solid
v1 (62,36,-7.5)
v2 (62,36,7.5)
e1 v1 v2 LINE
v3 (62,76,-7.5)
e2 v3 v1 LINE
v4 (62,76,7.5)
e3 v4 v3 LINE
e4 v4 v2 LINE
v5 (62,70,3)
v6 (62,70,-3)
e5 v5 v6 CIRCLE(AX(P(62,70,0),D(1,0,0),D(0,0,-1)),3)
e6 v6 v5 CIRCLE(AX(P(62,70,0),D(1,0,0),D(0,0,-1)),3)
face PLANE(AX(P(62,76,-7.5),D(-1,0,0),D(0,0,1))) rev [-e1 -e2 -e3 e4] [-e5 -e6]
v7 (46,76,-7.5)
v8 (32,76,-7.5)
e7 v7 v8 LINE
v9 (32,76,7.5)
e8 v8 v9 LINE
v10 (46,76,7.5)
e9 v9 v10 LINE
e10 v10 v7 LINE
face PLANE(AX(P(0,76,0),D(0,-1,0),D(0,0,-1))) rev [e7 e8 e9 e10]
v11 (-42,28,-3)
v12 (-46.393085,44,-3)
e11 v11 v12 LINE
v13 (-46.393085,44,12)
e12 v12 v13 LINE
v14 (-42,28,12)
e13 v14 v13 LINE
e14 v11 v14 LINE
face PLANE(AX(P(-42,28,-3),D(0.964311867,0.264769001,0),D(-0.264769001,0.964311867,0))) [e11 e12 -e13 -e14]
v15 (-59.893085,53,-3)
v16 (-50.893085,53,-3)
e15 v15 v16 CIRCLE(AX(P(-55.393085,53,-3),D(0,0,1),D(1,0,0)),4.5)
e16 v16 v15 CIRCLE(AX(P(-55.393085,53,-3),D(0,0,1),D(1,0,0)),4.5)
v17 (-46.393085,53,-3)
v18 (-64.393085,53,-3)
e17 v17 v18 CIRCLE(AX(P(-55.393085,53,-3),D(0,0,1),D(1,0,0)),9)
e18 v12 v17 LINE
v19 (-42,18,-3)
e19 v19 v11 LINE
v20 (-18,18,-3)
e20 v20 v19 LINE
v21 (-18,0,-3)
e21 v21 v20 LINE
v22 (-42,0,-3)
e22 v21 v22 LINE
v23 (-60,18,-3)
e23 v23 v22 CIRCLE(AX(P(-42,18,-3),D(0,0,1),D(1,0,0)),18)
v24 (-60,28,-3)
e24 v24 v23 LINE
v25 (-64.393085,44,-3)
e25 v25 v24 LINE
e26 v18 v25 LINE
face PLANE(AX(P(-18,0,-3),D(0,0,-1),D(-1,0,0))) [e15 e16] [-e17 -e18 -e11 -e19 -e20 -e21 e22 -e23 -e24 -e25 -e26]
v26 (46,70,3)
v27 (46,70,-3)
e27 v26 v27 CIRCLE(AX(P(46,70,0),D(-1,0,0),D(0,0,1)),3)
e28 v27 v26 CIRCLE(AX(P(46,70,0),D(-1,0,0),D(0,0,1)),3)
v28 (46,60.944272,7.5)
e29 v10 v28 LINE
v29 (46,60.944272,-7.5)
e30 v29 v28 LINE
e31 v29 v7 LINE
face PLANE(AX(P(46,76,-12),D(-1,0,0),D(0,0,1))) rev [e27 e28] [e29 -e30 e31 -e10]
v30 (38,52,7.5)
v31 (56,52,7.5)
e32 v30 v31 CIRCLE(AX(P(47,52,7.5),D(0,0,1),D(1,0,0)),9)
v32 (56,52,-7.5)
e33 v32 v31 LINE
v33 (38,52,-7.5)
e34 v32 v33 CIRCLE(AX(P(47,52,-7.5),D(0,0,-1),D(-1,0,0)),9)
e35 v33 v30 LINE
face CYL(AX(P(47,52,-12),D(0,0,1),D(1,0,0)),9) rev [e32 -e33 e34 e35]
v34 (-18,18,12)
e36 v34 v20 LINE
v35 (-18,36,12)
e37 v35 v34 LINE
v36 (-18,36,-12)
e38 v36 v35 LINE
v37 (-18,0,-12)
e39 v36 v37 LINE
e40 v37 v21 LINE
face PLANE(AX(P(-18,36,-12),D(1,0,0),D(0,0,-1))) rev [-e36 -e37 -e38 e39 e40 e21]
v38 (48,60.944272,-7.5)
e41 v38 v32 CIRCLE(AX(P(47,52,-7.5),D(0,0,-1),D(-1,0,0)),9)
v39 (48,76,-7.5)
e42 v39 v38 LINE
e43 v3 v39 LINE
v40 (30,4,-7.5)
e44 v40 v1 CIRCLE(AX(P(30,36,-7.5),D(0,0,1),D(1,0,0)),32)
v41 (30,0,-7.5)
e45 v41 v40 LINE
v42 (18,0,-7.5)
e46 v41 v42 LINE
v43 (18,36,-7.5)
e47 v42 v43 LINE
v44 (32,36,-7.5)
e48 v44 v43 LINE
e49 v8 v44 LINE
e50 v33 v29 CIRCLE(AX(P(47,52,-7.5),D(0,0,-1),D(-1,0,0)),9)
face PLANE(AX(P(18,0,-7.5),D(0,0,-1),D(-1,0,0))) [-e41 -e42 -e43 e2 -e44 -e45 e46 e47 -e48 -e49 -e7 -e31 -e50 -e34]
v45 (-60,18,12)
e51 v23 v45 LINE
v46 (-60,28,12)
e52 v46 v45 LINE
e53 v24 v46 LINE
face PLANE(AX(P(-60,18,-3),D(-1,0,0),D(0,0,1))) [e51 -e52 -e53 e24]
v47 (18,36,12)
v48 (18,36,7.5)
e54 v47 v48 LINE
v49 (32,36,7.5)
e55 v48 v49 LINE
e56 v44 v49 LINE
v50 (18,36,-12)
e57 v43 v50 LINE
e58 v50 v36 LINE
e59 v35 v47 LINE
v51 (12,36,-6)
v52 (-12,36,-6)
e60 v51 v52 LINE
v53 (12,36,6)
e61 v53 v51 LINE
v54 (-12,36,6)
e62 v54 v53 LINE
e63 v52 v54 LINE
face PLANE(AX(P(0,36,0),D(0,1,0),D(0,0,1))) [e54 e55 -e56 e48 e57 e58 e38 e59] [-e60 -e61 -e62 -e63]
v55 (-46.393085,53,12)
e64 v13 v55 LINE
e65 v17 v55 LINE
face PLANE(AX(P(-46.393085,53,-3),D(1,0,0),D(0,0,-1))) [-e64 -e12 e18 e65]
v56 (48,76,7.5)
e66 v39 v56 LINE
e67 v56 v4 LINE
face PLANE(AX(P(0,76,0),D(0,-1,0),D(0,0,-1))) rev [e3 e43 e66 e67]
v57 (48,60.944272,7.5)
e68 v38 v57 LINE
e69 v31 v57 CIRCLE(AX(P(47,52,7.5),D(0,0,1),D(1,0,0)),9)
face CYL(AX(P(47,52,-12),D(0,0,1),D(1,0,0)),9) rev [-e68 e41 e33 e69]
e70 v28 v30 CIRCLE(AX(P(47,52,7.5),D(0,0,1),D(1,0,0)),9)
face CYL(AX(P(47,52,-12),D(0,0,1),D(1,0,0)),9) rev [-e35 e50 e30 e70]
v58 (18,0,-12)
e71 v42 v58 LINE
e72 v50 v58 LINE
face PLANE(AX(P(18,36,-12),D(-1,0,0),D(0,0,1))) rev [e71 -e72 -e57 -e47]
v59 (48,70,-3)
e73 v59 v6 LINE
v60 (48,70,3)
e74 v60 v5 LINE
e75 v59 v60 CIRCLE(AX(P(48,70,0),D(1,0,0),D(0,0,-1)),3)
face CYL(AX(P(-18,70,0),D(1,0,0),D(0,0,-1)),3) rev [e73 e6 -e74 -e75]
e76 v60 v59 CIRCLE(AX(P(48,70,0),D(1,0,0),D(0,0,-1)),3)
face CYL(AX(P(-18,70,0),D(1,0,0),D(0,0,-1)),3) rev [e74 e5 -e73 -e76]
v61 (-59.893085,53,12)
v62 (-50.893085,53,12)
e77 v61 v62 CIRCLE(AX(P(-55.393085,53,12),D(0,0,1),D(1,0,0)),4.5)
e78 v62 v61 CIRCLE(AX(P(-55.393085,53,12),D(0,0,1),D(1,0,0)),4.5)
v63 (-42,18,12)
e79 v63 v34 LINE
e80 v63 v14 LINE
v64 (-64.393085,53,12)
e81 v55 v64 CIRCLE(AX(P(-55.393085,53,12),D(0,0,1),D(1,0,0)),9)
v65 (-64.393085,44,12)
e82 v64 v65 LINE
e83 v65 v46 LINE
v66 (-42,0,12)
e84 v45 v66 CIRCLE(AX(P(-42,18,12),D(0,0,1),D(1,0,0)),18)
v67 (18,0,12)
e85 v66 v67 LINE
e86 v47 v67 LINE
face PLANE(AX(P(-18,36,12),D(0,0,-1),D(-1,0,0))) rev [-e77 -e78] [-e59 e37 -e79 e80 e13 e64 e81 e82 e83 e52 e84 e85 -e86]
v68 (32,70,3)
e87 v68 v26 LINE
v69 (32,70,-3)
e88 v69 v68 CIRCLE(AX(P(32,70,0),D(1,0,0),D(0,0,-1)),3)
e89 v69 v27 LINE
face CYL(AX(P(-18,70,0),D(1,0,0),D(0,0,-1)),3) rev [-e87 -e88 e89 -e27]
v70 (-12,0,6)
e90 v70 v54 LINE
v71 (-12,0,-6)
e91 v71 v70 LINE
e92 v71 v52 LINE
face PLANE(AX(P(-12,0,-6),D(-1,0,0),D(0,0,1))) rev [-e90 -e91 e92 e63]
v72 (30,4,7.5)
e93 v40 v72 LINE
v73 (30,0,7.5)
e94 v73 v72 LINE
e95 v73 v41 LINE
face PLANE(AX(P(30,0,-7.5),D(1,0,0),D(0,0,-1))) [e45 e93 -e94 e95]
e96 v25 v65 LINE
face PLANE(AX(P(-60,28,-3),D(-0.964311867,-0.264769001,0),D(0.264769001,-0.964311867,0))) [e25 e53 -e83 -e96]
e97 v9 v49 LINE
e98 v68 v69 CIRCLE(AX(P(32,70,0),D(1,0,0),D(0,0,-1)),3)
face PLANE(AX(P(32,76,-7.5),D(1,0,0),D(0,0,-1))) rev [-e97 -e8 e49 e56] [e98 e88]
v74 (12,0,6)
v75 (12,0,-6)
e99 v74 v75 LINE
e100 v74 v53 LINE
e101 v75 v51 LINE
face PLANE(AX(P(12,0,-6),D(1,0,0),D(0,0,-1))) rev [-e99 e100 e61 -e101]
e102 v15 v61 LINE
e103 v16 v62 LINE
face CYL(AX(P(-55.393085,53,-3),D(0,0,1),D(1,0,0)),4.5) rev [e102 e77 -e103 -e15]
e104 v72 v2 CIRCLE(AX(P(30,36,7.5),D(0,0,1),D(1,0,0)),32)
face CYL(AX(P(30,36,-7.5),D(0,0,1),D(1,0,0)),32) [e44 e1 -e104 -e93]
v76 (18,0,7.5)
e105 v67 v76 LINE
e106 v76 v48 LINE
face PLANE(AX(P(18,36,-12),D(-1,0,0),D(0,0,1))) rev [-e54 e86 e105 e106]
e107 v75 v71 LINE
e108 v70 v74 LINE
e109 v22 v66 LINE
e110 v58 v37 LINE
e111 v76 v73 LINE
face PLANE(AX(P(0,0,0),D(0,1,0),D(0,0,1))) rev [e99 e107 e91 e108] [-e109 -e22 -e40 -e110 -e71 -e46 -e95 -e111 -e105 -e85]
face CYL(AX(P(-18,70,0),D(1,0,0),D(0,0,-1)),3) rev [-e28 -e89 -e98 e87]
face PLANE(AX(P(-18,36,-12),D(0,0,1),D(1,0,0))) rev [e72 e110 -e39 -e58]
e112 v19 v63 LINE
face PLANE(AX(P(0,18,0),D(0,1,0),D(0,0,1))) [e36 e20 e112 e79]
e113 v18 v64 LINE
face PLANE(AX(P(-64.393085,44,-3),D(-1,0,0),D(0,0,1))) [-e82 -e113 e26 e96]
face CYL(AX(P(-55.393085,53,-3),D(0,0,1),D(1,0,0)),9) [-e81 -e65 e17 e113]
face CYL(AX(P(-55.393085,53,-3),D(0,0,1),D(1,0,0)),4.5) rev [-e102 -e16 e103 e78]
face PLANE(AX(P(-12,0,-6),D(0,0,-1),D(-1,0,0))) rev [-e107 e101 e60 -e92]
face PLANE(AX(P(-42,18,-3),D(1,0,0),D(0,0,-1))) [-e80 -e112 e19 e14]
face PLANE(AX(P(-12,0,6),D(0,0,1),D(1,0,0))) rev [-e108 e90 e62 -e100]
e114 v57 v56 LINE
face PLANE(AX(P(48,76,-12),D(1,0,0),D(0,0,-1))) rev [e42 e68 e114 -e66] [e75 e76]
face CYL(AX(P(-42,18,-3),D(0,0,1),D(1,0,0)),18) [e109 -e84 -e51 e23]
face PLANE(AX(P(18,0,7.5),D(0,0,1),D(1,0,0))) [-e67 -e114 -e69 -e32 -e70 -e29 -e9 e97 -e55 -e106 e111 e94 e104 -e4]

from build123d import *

# Parameters (mm, degrees)
BASE_BLOCK_SKETCH_W                = 36
BASE_BLOCK_SKETCH_H                = 24
BASE_BLOCK_DEPTH                   = 36
RECTANGULAR_POCKET_12X6_DEPTH      = 43
RECTANGULAR_POCKET_12X6_DEPTH_BACK = 43
RECTANGULAR_POCKET_SKETCH_W        = 24
RECTANGULAR_POCKET_SKETCH_H        = 12
CLAMP_UPRIGHT_SKETCH_W             = 12
CLAMP_UPRIGHT_SKETCH_H             = 15
CLAMP_UPRIGHT_DEPTH                = 36
CURVED_ARM_DEPTH                   = 15
CLAMP_BLOCK_SKETCH_W               = 30
CLAMP_BLOCK_SKETCH_H               = 15
CLAMP_BLOCK_DEPTH                  = 40
CLAMP_SPLIT_SLOT_1MM_DEPTH         = 101.001249992
CLAMP_SPLIT_SLOT_1MM_DEPTH_BACK    = 101.001249992
CLAMP_CROSS_HOLE_DEPTH             = 111.995495404
CLAMP_CROSS_HOLE_DEPTH_BACK        = 111.995495404
CROSS_HOLE_SKETCH_R                = 3
SIDE_START                         = -18
SIDE_LUG_SKETCH_W                  = 24
SIDE_LUG_SKETCH_H                  = 15
SIDE_LUG_DEPTH                     = 18
ARM_SEGMENT_DEPTH                  = 15
ARM_LINK_DEPTH                     = 15
PIVOT_EYE_SKETCH_R                 = 4.5
PIVOT_EYE_DEPTH                    = 15


with BuildPart() as part:
    # Base Block Sketch → Base Block (new body)
    with BuildSketch(Plane(origin=(0, 0, 0), x_dir=(1, 0, 0), z_dir=(0, 1, 0))):
        Rectangle(BASE_BLOCK_SKETCH_W, BASE_BLOCK_SKETCH_H)
    extrude(amount=BASE_BLOCK_DEPTH)

    # Rectangular Pocket Sketch → Rectangular Pocket 12x6 (cut, two sides: drawn at the far end of the back side and taken through both)
    with BuildSketch(Plane(origin=(0, 36, 0), x_dir=(1, 0, 0), z_dir=(0, 1, 0)).offset(-RECTANGULAR_POCKET_12X6_DEPTH_BACK)):
        Rectangle(RECTANGULAR_POCKET_SKETCH_W, RECTANGULAR_POCKET_SKETCH_H)
    extrude(amount=RECTANGULAR_POCKET_12X6_DEPTH + RECTANGULAR_POCKET_12X6_DEPTH_BACK, mode=Mode.SUBTRACT)

    # Clamp Upright Sketch → Clamp Upright (add)
    with BuildSketch(Plane(origin=(0, 36, 0), x_dir=(1, 0, 0), z_dir=(0, 1, 0))):
        with Locations((24, 0)):
            Rectangle(CLAMP_UPRIGHT_SKETCH_W, CLAMP_UPRIGHT_SKETCH_H)
    extrude(amount=-CLAMP_UPRIGHT_DEPTH)

    # Curved Arm Sketch → Curved Arm (add)
    with BuildSketch(Plane.XY.offset(7.5)):
        with BuildLine():
            Line((30, 36), (62, 36))
            ThreePointArc((62, 36), (52.627416998, 13.372583002), (30, 4))
            Line((30, 4), (30, 36))
        make_face()
    extrude(amount=-CURVED_ARM_DEPTH)

    # Clamp Block Sketch → Clamp Block (add)
    with BuildSketch(Plane(origin=(0, 36, 0), x_dir=(1, 0, 0), z_dir=(0, 1, 0))):
        with Locations((47, 0)):
            Rectangle(CLAMP_BLOCK_SKETCH_W, CLAMP_BLOCK_SKETCH_H)
    extrude(amount=CLAMP_BLOCK_DEPTH)

    # Clamp Split Slot Sketch → Clamp Split Slot 1mm (cut, two sides: drawn at the far end of the back side and taken through both)
    with BuildSketch(Plane.XY.offset(7.5).offset(-CLAMP_SPLIT_SLOT_1MM_DEPTH_BACK)):
        with BuildLine():
            Line((46, 76), (46, 60.94427191))
            ThreePointArc((46, 60.94427191), (47, 43), (48, 60.94427191))
            Line((48, 60.94427191), (48, 76))
            Line((48, 76), (46, 76))
        make_face()
    extrude(amount=CLAMP_SPLIT_SLOT_1MM_DEPTH + CLAMP_SPLIT_SLOT_1MM_DEPTH_BACK, mode=Mode.SUBTRACT)

    # Cross Hole Sketch → Clamp Cross Hole (cut, two sides: drawn at the far end of the back side and taken through both)
    with BuildSketch(Plane(origin=(62, 0, 0), x_dir=(0, 0, -1), z_dir=(1, 0, 0)).offset(-CLAMP_CROSS_HOLE_DEPTH_BACK)):
        with Locations((0, 70)):
            Circle(CROSS_HOLE_SKETCH_R)
    extrude(amount=CLAMP_CROSS_HOLE_DEPTH + CLAMP_CROSS_HOLE_DEPTH_BACK, mode=Mode.SUBTRACT)

    # Side Lug Sketch → Side Lug (add)
    with BuildSketch(Plane(origin=(0, 36, 0), x_dir=(1, 0, 0), z_dir=(0, 1, 0)).offset(SIDE_START)):
        with Locations((-30, -4.5)):
            Rectangle(SIDE_LUG_SKETCH_W, SIDE_LUG_SKETCH_H)
    extrude(amount=-SIDE_LUG_DEPTH)

    # Arm Segment Sketch → Arm Segment (add)
    with BuildSketch(Plane.XY.offset(12)):
        with BuildLine():
            Line((-42, 18), (-42, 28))
            Line((-42, 28), (-60, 28))
            Line((-60, 28), (-60, 18))
            ThreePointArc((-60, 18), (-54.727922061, 5.272077939), (-42, 0))
            Line((-42, 0), (-42, 18))
        make_face()
    extrude(amount=-ARM_SEGMENT_DEPTH)

    # Arm Link Sketch → Arm Link (add)
    with BuildSketch(Plane.XY.offset(12)):
        Polygon((-60, 28), (-42, 28), (-46.393085021, 44), (-64.393085021, 44), align=None)
    extrude(amount=-ARM_LINK_DEPTH)

    # Pivot Eye Sketch → Pivot Eye (add)
    with BuildSketch(Plane.XY.offset(12)):
        with BuildLine():
            Line((-64.393085021, 44), (-64.393085021, 53))
            ThreePointArc((-64.393085021, 53), (-55.393085021, 62), (-46.393085021, 53))
            Line((-46.393085021, 53), (-46.393085021, 44))
            Line((-46.393085021, 44), (-64.393085021, 44))
        make_face()
        with Locations((-55.393085021, 53)):
            Circle(PIVOT_EYE_SKETCH_R, mode=Mode.SUBTRACT)
    extrude(amount=-PIVOT_EYE_DEPTH)


solid = part.part
